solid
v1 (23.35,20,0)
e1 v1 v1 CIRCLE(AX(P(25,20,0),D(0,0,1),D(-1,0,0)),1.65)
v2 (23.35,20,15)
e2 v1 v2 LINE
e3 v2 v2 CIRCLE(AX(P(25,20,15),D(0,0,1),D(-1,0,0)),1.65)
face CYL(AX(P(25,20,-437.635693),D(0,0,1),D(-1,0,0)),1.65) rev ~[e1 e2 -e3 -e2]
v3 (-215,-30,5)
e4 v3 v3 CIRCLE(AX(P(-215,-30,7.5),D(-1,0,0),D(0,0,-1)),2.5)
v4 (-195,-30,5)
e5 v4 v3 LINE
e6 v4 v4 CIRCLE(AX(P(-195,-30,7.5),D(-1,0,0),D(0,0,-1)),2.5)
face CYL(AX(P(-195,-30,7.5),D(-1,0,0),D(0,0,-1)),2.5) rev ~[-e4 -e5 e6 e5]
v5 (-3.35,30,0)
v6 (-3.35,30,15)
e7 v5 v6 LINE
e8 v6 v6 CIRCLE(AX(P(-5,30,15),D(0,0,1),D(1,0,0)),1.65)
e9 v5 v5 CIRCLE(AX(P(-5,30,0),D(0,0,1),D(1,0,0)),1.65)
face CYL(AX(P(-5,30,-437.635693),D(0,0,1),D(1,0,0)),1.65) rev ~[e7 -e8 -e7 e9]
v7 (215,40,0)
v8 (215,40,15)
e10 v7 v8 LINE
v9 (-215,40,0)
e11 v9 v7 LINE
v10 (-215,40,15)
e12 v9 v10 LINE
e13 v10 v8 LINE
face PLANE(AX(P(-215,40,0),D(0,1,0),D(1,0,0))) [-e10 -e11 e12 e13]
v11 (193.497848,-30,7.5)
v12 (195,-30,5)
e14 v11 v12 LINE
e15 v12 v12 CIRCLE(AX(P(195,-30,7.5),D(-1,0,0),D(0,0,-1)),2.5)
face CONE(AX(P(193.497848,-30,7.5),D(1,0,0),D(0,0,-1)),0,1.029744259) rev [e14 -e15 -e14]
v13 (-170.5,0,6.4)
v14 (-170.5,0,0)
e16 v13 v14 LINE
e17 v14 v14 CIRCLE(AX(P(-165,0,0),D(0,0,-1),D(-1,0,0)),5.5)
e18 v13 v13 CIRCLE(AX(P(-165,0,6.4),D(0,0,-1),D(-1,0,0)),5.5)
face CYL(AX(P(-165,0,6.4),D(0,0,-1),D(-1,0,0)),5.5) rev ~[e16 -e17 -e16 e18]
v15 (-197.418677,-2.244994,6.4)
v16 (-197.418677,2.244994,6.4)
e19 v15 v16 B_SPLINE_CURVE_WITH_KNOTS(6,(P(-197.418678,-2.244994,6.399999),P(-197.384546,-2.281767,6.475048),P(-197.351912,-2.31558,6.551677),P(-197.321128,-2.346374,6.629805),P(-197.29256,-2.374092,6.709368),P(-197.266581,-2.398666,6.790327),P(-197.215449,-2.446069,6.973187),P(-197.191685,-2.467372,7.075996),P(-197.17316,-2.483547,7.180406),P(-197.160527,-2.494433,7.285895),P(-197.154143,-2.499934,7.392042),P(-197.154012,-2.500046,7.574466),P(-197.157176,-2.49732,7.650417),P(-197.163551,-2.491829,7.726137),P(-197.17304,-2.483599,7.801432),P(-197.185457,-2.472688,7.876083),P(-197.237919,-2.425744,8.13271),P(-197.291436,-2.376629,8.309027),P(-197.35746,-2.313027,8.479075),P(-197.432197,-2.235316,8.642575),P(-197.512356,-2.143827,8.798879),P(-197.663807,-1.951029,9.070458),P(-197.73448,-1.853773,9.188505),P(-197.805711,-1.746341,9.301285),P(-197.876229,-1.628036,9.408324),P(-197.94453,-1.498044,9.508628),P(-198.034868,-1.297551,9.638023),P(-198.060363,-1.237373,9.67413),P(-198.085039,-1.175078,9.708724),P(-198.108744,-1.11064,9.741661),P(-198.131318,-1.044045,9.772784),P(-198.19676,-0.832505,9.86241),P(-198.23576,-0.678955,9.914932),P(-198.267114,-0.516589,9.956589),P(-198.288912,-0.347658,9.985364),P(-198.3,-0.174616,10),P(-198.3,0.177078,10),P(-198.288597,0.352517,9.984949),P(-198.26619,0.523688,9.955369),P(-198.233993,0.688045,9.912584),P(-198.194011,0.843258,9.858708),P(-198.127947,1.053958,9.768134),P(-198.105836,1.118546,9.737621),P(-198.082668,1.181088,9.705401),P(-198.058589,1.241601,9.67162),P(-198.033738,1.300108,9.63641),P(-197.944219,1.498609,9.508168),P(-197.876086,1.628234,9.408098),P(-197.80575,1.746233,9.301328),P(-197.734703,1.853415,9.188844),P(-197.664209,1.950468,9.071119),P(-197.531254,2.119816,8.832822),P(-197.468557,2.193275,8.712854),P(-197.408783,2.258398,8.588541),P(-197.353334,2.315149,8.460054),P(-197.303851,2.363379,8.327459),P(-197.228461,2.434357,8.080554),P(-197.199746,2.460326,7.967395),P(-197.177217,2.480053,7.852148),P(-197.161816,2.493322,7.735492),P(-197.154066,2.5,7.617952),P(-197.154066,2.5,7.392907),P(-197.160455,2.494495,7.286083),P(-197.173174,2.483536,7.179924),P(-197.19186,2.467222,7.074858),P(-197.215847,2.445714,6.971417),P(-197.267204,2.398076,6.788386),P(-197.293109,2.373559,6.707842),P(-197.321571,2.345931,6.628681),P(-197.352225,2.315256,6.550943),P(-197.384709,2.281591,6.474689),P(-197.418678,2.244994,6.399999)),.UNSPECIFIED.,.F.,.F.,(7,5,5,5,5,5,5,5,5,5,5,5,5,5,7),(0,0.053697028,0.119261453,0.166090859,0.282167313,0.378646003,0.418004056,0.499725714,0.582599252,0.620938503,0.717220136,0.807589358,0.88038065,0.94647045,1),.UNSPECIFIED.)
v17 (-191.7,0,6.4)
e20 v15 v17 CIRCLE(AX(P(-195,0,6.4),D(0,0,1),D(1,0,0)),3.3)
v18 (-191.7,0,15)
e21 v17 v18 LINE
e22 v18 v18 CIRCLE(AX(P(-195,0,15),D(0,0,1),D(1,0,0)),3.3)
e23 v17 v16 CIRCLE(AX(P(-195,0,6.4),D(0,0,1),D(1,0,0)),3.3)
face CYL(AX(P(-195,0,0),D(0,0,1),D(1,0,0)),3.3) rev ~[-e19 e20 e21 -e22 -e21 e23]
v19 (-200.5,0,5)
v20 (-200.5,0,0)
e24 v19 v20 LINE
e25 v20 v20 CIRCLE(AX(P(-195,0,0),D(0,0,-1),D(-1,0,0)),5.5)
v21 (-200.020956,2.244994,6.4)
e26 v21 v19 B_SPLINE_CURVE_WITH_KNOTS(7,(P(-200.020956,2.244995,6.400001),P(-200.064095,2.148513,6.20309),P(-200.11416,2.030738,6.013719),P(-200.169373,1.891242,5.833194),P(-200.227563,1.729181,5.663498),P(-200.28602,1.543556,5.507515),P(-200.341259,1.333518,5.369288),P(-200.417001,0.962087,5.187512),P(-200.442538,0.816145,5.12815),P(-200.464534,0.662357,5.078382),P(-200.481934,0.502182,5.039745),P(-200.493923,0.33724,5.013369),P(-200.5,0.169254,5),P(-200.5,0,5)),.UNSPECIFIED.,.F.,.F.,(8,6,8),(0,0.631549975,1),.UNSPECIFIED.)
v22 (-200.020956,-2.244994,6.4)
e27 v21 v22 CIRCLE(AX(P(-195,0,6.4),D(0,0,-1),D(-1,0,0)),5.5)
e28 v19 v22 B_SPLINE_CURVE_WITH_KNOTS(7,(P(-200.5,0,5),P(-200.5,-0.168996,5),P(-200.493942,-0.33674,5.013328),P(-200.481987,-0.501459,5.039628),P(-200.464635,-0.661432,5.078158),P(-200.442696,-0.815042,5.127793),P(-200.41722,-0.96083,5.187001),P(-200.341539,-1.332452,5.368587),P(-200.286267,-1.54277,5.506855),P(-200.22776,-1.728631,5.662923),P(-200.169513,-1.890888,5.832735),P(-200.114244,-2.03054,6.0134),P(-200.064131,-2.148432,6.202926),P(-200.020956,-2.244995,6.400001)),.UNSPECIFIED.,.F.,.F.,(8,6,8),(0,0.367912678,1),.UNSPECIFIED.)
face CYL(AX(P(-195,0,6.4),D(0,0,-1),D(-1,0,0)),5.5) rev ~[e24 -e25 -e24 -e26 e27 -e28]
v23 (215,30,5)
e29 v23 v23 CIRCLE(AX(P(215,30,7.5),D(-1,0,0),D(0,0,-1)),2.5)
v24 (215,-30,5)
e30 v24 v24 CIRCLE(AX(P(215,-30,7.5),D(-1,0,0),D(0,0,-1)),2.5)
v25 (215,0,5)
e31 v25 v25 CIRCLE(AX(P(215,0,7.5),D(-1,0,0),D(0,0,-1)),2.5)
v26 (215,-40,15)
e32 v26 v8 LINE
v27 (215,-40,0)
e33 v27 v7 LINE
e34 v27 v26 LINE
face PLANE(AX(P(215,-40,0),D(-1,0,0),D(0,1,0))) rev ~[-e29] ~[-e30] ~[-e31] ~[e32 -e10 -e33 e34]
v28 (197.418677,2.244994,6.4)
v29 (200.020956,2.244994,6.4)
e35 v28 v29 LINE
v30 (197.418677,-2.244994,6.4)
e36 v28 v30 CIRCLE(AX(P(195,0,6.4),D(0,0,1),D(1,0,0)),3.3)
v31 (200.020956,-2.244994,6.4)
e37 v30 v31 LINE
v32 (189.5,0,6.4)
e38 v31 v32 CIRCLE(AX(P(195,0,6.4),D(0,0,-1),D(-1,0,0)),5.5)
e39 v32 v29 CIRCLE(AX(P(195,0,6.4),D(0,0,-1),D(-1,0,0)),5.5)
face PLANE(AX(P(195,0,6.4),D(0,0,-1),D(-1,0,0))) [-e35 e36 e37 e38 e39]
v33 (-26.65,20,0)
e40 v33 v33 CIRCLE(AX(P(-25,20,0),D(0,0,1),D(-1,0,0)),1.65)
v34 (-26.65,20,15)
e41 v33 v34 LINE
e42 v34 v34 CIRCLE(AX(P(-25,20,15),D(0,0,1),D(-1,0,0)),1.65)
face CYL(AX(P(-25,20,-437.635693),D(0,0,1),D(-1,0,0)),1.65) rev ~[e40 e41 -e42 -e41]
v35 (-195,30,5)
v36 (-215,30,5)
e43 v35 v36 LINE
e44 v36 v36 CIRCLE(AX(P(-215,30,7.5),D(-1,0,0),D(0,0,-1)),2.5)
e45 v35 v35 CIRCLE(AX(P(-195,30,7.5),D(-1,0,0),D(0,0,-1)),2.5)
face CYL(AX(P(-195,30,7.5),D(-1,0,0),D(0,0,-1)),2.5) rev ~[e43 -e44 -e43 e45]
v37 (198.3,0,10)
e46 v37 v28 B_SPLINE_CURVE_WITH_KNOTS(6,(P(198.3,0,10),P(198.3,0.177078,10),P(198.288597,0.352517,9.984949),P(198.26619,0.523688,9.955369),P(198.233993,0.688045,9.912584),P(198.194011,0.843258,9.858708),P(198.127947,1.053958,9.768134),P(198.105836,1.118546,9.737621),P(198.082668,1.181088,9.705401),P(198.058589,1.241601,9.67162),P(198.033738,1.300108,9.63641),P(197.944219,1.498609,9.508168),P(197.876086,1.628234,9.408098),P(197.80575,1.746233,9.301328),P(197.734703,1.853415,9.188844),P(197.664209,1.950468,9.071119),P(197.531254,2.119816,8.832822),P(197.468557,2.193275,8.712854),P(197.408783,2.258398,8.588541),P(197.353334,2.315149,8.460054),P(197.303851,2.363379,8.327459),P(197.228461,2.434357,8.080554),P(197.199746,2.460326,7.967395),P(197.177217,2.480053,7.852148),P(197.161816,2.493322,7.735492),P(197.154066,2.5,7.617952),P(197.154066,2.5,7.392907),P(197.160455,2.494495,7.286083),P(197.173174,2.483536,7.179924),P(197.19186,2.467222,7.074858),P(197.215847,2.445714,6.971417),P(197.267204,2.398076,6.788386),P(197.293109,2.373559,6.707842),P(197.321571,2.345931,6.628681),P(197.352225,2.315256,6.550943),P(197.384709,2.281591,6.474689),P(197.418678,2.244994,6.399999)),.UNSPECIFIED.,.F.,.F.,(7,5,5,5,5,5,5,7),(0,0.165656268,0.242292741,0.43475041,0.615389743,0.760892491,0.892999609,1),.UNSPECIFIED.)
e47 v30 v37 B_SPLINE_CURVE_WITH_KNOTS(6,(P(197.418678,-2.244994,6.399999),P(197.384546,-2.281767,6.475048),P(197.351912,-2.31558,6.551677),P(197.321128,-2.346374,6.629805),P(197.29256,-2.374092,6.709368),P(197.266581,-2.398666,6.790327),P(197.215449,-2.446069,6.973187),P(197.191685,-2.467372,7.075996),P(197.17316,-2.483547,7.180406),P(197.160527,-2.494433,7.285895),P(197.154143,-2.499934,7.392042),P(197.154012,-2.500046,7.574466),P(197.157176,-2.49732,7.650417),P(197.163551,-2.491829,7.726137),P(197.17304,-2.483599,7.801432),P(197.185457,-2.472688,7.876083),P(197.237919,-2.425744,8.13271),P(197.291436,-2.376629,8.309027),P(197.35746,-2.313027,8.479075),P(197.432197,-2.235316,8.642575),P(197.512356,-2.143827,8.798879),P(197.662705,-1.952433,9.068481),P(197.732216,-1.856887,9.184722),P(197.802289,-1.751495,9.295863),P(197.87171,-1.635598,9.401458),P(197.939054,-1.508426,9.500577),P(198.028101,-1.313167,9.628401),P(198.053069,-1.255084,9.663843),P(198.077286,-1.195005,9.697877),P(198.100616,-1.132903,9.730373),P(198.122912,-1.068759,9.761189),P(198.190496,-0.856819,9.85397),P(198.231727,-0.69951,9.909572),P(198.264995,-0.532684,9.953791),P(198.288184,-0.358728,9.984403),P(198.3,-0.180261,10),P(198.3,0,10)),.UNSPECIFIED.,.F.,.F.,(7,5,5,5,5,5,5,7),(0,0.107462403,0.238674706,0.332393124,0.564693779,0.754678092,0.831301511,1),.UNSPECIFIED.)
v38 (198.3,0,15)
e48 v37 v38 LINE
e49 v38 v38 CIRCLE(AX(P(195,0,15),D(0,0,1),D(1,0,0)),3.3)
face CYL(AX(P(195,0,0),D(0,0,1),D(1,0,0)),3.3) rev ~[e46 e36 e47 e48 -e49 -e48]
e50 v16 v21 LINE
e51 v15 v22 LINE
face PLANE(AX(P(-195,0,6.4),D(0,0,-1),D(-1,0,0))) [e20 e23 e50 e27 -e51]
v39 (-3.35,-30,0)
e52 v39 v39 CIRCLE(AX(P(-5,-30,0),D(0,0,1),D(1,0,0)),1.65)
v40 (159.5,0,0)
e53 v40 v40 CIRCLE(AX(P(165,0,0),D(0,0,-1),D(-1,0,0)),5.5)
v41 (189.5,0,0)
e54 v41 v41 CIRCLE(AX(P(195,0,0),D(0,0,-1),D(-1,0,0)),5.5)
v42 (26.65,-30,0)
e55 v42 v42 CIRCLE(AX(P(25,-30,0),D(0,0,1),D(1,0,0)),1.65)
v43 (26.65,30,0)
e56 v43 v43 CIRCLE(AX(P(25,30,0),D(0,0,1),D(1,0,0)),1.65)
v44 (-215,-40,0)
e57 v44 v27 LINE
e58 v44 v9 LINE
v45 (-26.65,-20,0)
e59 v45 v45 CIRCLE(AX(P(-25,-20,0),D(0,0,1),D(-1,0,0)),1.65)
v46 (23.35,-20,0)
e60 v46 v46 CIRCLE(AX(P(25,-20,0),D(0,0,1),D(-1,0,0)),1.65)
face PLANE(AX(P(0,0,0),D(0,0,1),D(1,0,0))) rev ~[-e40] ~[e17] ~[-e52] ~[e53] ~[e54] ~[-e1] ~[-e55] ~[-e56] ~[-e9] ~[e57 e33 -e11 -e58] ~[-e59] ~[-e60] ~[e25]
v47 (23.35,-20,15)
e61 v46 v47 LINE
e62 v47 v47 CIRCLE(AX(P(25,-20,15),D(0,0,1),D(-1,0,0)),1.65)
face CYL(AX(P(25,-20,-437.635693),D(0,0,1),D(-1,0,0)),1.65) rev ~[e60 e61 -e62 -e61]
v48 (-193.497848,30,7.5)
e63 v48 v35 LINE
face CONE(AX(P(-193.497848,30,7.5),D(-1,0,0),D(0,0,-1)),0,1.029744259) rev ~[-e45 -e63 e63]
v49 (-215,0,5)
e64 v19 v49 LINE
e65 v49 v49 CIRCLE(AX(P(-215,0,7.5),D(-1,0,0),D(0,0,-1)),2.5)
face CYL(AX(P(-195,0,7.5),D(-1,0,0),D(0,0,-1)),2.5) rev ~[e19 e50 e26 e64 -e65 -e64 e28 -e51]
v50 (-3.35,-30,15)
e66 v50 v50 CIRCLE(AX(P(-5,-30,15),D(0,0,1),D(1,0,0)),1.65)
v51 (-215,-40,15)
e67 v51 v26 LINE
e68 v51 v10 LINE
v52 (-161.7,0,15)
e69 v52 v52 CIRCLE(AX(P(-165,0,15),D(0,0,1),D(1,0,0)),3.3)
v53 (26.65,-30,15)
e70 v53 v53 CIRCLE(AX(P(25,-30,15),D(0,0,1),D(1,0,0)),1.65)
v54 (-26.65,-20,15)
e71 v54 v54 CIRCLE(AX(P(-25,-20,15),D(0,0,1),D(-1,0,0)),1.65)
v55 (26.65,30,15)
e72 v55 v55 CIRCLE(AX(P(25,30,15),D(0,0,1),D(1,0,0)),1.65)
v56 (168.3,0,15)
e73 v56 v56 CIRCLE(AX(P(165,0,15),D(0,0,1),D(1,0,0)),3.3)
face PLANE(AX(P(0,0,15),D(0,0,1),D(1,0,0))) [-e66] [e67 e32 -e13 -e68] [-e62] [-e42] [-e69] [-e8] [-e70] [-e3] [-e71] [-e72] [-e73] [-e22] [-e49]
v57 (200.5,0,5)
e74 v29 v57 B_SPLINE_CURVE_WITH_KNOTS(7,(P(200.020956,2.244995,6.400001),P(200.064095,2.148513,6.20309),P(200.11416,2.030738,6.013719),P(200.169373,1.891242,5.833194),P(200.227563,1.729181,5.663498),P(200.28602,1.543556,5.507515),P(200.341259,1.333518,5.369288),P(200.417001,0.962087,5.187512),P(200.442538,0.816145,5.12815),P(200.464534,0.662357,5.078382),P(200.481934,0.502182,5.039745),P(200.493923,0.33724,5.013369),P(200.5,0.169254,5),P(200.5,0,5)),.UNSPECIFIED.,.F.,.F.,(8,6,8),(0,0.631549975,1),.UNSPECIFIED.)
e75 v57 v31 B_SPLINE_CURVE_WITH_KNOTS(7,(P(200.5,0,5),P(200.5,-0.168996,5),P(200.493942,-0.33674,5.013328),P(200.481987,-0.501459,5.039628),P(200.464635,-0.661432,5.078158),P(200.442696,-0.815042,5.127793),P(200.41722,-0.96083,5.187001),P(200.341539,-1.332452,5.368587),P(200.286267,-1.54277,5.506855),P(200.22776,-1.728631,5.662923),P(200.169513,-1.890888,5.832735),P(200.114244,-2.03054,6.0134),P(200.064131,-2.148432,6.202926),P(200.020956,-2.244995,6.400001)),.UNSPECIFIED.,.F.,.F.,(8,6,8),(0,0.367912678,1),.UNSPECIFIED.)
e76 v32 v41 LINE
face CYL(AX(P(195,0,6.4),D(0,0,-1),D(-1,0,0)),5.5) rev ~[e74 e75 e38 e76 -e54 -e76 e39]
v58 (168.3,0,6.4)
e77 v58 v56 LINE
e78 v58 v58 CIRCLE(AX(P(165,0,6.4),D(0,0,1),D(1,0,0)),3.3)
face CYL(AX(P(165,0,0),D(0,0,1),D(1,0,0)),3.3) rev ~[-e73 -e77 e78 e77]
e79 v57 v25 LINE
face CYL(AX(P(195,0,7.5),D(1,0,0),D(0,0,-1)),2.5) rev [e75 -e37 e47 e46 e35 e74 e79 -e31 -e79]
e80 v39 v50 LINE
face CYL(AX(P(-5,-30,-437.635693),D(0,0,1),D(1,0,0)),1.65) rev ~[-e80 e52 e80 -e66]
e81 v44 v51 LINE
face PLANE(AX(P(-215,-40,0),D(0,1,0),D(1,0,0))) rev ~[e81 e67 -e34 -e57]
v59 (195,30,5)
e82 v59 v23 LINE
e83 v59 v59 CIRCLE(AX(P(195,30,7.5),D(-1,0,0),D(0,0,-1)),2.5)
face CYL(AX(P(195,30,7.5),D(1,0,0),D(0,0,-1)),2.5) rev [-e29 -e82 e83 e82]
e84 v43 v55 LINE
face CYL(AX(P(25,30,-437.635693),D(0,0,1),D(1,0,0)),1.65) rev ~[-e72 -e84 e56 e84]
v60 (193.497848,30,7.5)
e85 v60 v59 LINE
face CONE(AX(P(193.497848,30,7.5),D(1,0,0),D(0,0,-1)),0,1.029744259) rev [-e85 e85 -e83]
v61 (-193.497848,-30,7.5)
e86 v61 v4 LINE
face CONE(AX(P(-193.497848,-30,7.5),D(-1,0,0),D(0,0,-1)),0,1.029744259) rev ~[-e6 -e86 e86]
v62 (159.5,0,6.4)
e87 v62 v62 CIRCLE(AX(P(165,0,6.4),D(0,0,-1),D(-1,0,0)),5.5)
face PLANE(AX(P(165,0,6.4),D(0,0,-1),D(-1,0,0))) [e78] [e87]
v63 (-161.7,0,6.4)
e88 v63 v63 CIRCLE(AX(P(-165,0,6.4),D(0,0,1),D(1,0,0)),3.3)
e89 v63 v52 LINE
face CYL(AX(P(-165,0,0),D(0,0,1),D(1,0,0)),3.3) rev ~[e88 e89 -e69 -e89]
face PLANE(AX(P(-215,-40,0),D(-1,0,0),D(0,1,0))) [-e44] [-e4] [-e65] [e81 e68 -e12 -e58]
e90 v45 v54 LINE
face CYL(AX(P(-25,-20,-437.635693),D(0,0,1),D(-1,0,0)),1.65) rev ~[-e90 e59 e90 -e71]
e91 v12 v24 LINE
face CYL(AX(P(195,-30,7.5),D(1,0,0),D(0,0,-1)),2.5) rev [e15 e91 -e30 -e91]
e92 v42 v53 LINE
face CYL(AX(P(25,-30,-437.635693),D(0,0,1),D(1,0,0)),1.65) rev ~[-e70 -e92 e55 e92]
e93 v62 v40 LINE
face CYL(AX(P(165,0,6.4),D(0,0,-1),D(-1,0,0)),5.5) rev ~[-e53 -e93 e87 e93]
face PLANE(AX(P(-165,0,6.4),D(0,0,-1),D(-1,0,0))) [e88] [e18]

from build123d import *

# Parameters (mm, degrees)
SKETCH_1_W                   = 430
SKETCH_1_H                   = 80
EXTRUDE_1_DEPTH              = 15
HOLE_WIZARD_M4_6_D           = 3.3
HOLE_WIZARD_M4_7_D           = 3.3
HOLE_WIZARD_M4_5_D           = 6.6
HOLE_WIZARD_M4_5_CBORE_D     = 11
HOLE_WIZARD_M4_5_CBORE_DEPTH = 6.4
HOLE_WIZARD_M6_1_AT_2_COUNT  = 2
HOLE_WIZARD_M6_1_AT_2_PITCH  = 30
HOLE_WIZARD_M6_1_AT_3_COUNT  = 2
HOLE_WIZARD_M6_1_AT_3_PITCH  = 60


with BuildPart() as part:
    # 草图1 → 凸台-拉伸1 (new body)
    with BuildSketch(Plane.XY):
        Rectangle(SKETCH_1_W, SKETCH_1_H)
    extrude(amount=EXTRUDE_1_DEPTH)

    # M4 螺纹孔6 (through all)
    with Locations(Plane(origin=(0, 0, 0), x_dir=(1, 0, 0), z_dir=(0, 0, -1))):
        with Locations((25, 20), (-25, 20), (-25, -20), (25, -20)):
            Hole(HOLE_WIZARD_M4_6_D / 2)

    # M4 螺纹孔7 (through all)
    with Locations(Plane(origin=(0, 0, 0), x_dir=(-1, 0, 0), z_dir=(0, 0, -1))):
        with Locations((5, 30), (5, -30), (-25, 30), (-25, -30)):
            Hole(HOLE_WIZARD_M4_7_D / 2)

    # M4 六角凹头螺钉的柱形沉头孔5 (through all)
    with Locations(Plane(origin=(0, 0, 0), x_dir=(-1, 0, 0), z_dir=(0, 0, -1))):
        with Locations((-195, 0), (-165, 0), (165, 0), (195, 0)):
            CounterBoreHole(HOLE_WIZARD_M4_5_D / 2, HOLE_WIZARD_M4_5_CBORE_D / 2, HOLE_WIZARD_M4_5_CBORE_DEPTH)

    # 草图35 → M6 螺纹孔1 (revolve, cut)
    with BuildSketch(Plane(origin=(215, 30, 7.5), x_dir=(0, 0, -1), z_dir=(0, 1, 0))):
        Polygon((0, 0), (0, 21.502151548), (2.5, 20), (2.5, 0), align=None)
    hole_wizard_m6_1 = revolve(axis=Axis((221.35, 30, 7.5), (-1, 0, 0)), mode=Mode.SUBTRACT)

    # M6 螺纹孔1 at 2: M6 螺纹孔1 ×2
    with Locations(*[(0, -i * HOLE_WIZARD_M6_1_AT_2_PITCH, 0) for i in range(1, HOLE_WIZARD_M6_1_AT_2_COUNT)]):
        add(hole_wizard_m6_1, mode=Mode.SUBTRACT)

    # M6 螺纹孔1 at 3: M6 螺纹孔1 ×2
    with Locations(*[(0, -i * HOLE_WIZARD_M6_1_AT_3_PITCH, 0) for i in range(1, HOLE_WIZARD_M6_1_AT_3_COUNT)]):
        add(hole_wizard_m6_1, mode=Mode.SUBTRACT)

    # 镜向1: M6 螺纹孔1 across plane
    add(hole_wizard_m6_1.mirror(Plane(origin=(0, 0, 0), x_dir=(0, 0, 1), z_dir=(1, 0, 0))), mode=Mode.SUBTRACT)

    # 镜向1 copy 1 sketch → 镜向1 copy 1 (revolve, cut)
    with BuildSketch(Plane(origin=(-215, 0, 7.5), x_dir=(0, 0, -1), z_dir=(0, 1, 0))):
        Polygon((0, 0), (0, -21.502151548), (2.5, -20), (2.5, 0), align=None)
    revolve(axis=Axis((-221.35, 0, 7.5), (-1, 0, 0)), mode=Mode.SUBTRACT)

    # 镜向1 copy 2 sketch → 镜向1 copy 2 (revolve, cut)
    with BuildSketch(Plane(origin=(-215, -30, 7.5), x_dir=(0, 0, -1), z_dir=(0, 1, 0))):
        Polygon((0, 0), (0, -21.502151548), (2.5, -20), (2.5, 0), align=None)
    revolve(axis=Axis((-221.35, -30, 7.5), (-1, 0, 0)), mode=Mode.SUBTRACT)


solid = part.part
